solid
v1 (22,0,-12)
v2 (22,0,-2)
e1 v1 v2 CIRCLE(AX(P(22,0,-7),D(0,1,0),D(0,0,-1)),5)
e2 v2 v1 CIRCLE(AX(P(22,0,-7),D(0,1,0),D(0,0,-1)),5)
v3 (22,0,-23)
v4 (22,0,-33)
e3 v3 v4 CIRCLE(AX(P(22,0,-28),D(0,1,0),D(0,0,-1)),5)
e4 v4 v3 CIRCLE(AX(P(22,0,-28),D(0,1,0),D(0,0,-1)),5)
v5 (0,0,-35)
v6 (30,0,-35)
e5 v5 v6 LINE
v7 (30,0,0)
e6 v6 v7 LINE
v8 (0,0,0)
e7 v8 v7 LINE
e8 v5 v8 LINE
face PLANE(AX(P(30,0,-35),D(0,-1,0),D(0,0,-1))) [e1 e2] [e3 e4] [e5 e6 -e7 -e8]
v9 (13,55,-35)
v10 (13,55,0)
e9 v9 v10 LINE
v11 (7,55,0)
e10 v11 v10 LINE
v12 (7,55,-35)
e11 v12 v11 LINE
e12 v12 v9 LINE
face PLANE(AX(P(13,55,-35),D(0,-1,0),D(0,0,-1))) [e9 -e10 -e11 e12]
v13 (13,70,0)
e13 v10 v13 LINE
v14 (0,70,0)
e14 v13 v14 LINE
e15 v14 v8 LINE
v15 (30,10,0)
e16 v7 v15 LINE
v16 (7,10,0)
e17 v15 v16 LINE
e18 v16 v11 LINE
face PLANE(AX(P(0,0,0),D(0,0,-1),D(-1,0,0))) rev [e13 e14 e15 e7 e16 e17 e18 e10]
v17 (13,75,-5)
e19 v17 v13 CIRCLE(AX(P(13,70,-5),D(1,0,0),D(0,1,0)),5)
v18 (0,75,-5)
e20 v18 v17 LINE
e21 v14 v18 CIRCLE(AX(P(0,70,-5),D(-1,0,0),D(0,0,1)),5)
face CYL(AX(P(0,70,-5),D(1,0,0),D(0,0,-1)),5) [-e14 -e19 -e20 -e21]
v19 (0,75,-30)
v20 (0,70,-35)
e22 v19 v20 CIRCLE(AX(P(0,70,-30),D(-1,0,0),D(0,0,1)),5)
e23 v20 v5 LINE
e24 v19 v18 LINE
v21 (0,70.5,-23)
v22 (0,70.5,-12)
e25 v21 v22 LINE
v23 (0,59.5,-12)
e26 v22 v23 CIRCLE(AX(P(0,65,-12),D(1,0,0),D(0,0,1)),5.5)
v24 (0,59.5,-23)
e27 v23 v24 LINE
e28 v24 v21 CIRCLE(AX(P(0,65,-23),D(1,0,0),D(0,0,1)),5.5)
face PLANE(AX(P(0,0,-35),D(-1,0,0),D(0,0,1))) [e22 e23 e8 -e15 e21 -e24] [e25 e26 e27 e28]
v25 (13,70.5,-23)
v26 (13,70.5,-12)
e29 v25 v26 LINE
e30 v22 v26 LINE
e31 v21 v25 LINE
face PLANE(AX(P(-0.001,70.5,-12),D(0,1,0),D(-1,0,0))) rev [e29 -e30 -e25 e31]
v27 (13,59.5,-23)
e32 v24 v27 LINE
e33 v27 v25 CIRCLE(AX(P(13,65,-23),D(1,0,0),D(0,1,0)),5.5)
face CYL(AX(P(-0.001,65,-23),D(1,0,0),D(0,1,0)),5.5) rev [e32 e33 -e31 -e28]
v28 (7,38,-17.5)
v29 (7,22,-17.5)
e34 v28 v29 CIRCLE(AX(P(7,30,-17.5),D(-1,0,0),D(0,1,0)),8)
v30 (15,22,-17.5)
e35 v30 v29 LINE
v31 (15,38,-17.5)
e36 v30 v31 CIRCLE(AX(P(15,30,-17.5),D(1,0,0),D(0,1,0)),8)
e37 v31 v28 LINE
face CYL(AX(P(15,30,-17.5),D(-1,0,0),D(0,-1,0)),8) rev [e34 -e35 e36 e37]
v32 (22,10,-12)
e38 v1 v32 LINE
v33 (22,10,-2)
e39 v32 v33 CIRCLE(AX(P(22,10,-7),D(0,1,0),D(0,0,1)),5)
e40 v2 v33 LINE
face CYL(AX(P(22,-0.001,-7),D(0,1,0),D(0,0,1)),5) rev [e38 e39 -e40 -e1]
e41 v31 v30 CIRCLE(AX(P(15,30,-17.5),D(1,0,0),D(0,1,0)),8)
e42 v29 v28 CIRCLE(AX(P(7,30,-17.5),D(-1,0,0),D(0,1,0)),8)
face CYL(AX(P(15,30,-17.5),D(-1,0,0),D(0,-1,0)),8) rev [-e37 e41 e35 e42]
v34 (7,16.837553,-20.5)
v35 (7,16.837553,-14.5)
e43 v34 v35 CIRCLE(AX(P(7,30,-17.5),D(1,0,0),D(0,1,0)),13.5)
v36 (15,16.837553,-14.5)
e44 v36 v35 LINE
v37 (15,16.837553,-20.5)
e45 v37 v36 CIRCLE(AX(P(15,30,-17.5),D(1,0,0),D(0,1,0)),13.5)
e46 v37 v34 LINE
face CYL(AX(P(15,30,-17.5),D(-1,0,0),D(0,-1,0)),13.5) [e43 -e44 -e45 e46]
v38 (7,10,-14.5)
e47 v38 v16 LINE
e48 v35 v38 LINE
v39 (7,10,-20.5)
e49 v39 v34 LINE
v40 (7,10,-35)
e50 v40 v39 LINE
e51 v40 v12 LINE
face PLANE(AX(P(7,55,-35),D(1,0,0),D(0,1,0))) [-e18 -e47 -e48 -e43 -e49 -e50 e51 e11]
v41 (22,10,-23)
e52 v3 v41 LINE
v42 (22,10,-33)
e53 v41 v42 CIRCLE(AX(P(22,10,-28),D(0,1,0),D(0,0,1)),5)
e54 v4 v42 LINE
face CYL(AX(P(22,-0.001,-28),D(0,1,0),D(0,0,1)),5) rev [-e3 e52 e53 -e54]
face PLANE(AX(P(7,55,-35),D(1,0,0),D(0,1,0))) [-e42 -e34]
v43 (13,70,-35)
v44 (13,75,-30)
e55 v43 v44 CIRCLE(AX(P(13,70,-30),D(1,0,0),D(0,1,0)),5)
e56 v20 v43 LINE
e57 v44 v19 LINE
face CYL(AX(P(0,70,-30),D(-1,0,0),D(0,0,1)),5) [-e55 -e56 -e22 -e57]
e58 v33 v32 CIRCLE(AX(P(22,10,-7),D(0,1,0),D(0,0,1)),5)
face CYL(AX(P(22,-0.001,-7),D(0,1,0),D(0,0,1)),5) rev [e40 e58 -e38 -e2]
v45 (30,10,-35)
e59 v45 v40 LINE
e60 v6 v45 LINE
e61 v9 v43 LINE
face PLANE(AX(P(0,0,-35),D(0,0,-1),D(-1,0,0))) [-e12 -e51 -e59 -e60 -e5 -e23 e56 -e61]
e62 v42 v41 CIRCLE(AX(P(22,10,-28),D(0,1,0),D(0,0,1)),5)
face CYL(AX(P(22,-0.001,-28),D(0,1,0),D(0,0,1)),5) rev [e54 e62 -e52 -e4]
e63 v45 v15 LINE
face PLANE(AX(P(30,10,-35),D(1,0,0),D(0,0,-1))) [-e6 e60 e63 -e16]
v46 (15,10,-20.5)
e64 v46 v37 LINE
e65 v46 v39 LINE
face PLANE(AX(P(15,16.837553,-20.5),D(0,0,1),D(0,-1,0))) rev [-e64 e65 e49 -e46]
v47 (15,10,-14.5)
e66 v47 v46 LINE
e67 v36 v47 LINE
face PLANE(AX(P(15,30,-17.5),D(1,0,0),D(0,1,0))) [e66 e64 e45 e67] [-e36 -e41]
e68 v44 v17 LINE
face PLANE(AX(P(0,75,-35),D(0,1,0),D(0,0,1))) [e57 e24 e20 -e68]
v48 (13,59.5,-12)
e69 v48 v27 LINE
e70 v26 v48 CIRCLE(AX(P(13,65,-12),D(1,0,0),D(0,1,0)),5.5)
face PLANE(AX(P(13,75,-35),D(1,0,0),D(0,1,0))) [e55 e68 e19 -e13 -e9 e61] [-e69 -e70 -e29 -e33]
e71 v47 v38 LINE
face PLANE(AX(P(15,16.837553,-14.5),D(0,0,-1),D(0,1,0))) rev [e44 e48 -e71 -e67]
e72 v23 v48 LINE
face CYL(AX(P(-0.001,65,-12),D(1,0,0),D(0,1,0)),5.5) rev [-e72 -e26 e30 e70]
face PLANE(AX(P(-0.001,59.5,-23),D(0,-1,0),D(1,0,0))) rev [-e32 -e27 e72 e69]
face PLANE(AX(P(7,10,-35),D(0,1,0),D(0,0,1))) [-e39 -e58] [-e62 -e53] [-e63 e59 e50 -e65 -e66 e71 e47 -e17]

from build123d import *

# Parameters (mm, degrees)
BRACKET_BODY_DEPTH   = 35
BASE_HOLES_CUT_REACH = 81.687
BASE_HOLES_SKETCH_R  = 5
RING_BOSS_SKETCH_R   = 8
RING_BOSS_DEPTH      = 8
TOP_EDGE_FILLET_R5_R = 5
TOP_SLOT_CUT_REACH   = 86.493


with BuildPart() as part:
    # Bracket Profile Sketch → Bracket Body (new body)
    with BuildSketch(Plane.XY):
        Polygon((0, 0), (0, 75), (13, 75), (13, 55), (7, 55), (7, 10), (30, 10), (30, 0), align=None)
    extrude(amount=-BRACKET_BODY_DEPTH)

    # Base Holes Sketch → Base Holes Cut (cut, up to next)
    with BuildSketch(Plane(origin=(0, 10, 0), x_dir=(1, 0, 0), z_dir=(0, 1, 0)), mode=Mode.PRIVATE) as base_holes_cut_sk1:
        with Locations(Location((22, 28, 0), (0, 0, 270))):
            Circle(BASE_HOLES_SKETCH_R)
    base_holes_cut_tool1 = extrude(base_holes_cut_sk1.sketch, amount=-BASE_HOLES_CUT_REACH, mode=Mode.PRIVATE) & part.part
    # Base Holes Sketch → Base Holes Cut (cut, up to next)
    with BuildSketch(Plane(origin=(0, 10, 0), x_dir=(1, 0, 0), z_dir=(0, 1, 0)), mode=Mode.PRIVATE) as base_holes_cut_sk2:
        with Locations(Location((22, 7, 0), (0, 0, 270))):
            Circle(BASE_HOLES_SKETCH_R)
    base_holes_cut_tool2 = extrude(base_holes_cut_sk2.sketch, amount=-BASE_HOLES_CUT_REACH, mode=Mode.PRIVATE) & part.part
    add(base_holes_cut_tool1.solids().sort_by_distance((22, 10, -28))[0], mode=Mode.SUBTRACT)
    add(base_holes_cut_tool2.solids().sort_by_distance((22, 10, -7))[0], mode=Mode.SUBTRACT)

    # Ring Boss Sketch → Ring Boss (add)
    with BuildSketch(Plane(origin=(7, 0, 0), x_dir=(0, 0, -1), z_dir=(1, 0, 0))):
        with BuildLine():
            Line((14.5, 16.837553419), (14.5, 10))
            Line((14.5, 10), (20.5, 10))
            Line((20.5, 10), (20.5, 16.837553419))
            ThreePointArc((20.5, 16.837553419), (17.5, 43.5), (14.5, 16.837553419))
        make_face()
        with Locations(Location((17.5, 30, 0), (0, 0, 90))):
            Circle(RING_BOSS_SKETCH_R, mode=Mode.SUBTRACT)
    extrude(amount=RING_BOSS_DEPTH)

    # Top Edge Fillet R5
    top_edge_fillet_r5_edges = [part.edges().sort_by_distance(p)[0] for p in [
        (6.5, 75, -35),
        (6.5, 75, 0),
    ]]
    fillet(top_edge_fillet_r5_edges, radius=TOP_EDGE_FILLET_R5_R)

    # Top Slot Sketch → Top Slot Cut (cut, up to next)
    with BuildSketch(Plane(origin=(13, 0, 0), x_dir=(0, 0, -1), z_dir=(1, 0, 0)), mode=Mode.PRIVATE) as top_slot_cut_sk1:
        with BuildLine():
            Line((12, 70.5), (23, 70.5))
            ThreePointArc((23, 70.5), (28.5, 65), (23, 59.5))
            Line((23, 59.5), (12, 59.5))
            ThreePointArc((12, 59.5), (6.5, 65), (12, 70.5))
        make_face()
    top_slot_cut_tool1 = extrude(top_slot_cut_sk1.sketch, amount=-TOP_SLOT_CUT_REACH, mode=Mode.PRIVATE) & part.part
    add(top_slot_cut_tool1.solids().sort_by_distance((13, 65, -17.5))[0], mode=Mode.SUBTRACT)


solid = part.part
